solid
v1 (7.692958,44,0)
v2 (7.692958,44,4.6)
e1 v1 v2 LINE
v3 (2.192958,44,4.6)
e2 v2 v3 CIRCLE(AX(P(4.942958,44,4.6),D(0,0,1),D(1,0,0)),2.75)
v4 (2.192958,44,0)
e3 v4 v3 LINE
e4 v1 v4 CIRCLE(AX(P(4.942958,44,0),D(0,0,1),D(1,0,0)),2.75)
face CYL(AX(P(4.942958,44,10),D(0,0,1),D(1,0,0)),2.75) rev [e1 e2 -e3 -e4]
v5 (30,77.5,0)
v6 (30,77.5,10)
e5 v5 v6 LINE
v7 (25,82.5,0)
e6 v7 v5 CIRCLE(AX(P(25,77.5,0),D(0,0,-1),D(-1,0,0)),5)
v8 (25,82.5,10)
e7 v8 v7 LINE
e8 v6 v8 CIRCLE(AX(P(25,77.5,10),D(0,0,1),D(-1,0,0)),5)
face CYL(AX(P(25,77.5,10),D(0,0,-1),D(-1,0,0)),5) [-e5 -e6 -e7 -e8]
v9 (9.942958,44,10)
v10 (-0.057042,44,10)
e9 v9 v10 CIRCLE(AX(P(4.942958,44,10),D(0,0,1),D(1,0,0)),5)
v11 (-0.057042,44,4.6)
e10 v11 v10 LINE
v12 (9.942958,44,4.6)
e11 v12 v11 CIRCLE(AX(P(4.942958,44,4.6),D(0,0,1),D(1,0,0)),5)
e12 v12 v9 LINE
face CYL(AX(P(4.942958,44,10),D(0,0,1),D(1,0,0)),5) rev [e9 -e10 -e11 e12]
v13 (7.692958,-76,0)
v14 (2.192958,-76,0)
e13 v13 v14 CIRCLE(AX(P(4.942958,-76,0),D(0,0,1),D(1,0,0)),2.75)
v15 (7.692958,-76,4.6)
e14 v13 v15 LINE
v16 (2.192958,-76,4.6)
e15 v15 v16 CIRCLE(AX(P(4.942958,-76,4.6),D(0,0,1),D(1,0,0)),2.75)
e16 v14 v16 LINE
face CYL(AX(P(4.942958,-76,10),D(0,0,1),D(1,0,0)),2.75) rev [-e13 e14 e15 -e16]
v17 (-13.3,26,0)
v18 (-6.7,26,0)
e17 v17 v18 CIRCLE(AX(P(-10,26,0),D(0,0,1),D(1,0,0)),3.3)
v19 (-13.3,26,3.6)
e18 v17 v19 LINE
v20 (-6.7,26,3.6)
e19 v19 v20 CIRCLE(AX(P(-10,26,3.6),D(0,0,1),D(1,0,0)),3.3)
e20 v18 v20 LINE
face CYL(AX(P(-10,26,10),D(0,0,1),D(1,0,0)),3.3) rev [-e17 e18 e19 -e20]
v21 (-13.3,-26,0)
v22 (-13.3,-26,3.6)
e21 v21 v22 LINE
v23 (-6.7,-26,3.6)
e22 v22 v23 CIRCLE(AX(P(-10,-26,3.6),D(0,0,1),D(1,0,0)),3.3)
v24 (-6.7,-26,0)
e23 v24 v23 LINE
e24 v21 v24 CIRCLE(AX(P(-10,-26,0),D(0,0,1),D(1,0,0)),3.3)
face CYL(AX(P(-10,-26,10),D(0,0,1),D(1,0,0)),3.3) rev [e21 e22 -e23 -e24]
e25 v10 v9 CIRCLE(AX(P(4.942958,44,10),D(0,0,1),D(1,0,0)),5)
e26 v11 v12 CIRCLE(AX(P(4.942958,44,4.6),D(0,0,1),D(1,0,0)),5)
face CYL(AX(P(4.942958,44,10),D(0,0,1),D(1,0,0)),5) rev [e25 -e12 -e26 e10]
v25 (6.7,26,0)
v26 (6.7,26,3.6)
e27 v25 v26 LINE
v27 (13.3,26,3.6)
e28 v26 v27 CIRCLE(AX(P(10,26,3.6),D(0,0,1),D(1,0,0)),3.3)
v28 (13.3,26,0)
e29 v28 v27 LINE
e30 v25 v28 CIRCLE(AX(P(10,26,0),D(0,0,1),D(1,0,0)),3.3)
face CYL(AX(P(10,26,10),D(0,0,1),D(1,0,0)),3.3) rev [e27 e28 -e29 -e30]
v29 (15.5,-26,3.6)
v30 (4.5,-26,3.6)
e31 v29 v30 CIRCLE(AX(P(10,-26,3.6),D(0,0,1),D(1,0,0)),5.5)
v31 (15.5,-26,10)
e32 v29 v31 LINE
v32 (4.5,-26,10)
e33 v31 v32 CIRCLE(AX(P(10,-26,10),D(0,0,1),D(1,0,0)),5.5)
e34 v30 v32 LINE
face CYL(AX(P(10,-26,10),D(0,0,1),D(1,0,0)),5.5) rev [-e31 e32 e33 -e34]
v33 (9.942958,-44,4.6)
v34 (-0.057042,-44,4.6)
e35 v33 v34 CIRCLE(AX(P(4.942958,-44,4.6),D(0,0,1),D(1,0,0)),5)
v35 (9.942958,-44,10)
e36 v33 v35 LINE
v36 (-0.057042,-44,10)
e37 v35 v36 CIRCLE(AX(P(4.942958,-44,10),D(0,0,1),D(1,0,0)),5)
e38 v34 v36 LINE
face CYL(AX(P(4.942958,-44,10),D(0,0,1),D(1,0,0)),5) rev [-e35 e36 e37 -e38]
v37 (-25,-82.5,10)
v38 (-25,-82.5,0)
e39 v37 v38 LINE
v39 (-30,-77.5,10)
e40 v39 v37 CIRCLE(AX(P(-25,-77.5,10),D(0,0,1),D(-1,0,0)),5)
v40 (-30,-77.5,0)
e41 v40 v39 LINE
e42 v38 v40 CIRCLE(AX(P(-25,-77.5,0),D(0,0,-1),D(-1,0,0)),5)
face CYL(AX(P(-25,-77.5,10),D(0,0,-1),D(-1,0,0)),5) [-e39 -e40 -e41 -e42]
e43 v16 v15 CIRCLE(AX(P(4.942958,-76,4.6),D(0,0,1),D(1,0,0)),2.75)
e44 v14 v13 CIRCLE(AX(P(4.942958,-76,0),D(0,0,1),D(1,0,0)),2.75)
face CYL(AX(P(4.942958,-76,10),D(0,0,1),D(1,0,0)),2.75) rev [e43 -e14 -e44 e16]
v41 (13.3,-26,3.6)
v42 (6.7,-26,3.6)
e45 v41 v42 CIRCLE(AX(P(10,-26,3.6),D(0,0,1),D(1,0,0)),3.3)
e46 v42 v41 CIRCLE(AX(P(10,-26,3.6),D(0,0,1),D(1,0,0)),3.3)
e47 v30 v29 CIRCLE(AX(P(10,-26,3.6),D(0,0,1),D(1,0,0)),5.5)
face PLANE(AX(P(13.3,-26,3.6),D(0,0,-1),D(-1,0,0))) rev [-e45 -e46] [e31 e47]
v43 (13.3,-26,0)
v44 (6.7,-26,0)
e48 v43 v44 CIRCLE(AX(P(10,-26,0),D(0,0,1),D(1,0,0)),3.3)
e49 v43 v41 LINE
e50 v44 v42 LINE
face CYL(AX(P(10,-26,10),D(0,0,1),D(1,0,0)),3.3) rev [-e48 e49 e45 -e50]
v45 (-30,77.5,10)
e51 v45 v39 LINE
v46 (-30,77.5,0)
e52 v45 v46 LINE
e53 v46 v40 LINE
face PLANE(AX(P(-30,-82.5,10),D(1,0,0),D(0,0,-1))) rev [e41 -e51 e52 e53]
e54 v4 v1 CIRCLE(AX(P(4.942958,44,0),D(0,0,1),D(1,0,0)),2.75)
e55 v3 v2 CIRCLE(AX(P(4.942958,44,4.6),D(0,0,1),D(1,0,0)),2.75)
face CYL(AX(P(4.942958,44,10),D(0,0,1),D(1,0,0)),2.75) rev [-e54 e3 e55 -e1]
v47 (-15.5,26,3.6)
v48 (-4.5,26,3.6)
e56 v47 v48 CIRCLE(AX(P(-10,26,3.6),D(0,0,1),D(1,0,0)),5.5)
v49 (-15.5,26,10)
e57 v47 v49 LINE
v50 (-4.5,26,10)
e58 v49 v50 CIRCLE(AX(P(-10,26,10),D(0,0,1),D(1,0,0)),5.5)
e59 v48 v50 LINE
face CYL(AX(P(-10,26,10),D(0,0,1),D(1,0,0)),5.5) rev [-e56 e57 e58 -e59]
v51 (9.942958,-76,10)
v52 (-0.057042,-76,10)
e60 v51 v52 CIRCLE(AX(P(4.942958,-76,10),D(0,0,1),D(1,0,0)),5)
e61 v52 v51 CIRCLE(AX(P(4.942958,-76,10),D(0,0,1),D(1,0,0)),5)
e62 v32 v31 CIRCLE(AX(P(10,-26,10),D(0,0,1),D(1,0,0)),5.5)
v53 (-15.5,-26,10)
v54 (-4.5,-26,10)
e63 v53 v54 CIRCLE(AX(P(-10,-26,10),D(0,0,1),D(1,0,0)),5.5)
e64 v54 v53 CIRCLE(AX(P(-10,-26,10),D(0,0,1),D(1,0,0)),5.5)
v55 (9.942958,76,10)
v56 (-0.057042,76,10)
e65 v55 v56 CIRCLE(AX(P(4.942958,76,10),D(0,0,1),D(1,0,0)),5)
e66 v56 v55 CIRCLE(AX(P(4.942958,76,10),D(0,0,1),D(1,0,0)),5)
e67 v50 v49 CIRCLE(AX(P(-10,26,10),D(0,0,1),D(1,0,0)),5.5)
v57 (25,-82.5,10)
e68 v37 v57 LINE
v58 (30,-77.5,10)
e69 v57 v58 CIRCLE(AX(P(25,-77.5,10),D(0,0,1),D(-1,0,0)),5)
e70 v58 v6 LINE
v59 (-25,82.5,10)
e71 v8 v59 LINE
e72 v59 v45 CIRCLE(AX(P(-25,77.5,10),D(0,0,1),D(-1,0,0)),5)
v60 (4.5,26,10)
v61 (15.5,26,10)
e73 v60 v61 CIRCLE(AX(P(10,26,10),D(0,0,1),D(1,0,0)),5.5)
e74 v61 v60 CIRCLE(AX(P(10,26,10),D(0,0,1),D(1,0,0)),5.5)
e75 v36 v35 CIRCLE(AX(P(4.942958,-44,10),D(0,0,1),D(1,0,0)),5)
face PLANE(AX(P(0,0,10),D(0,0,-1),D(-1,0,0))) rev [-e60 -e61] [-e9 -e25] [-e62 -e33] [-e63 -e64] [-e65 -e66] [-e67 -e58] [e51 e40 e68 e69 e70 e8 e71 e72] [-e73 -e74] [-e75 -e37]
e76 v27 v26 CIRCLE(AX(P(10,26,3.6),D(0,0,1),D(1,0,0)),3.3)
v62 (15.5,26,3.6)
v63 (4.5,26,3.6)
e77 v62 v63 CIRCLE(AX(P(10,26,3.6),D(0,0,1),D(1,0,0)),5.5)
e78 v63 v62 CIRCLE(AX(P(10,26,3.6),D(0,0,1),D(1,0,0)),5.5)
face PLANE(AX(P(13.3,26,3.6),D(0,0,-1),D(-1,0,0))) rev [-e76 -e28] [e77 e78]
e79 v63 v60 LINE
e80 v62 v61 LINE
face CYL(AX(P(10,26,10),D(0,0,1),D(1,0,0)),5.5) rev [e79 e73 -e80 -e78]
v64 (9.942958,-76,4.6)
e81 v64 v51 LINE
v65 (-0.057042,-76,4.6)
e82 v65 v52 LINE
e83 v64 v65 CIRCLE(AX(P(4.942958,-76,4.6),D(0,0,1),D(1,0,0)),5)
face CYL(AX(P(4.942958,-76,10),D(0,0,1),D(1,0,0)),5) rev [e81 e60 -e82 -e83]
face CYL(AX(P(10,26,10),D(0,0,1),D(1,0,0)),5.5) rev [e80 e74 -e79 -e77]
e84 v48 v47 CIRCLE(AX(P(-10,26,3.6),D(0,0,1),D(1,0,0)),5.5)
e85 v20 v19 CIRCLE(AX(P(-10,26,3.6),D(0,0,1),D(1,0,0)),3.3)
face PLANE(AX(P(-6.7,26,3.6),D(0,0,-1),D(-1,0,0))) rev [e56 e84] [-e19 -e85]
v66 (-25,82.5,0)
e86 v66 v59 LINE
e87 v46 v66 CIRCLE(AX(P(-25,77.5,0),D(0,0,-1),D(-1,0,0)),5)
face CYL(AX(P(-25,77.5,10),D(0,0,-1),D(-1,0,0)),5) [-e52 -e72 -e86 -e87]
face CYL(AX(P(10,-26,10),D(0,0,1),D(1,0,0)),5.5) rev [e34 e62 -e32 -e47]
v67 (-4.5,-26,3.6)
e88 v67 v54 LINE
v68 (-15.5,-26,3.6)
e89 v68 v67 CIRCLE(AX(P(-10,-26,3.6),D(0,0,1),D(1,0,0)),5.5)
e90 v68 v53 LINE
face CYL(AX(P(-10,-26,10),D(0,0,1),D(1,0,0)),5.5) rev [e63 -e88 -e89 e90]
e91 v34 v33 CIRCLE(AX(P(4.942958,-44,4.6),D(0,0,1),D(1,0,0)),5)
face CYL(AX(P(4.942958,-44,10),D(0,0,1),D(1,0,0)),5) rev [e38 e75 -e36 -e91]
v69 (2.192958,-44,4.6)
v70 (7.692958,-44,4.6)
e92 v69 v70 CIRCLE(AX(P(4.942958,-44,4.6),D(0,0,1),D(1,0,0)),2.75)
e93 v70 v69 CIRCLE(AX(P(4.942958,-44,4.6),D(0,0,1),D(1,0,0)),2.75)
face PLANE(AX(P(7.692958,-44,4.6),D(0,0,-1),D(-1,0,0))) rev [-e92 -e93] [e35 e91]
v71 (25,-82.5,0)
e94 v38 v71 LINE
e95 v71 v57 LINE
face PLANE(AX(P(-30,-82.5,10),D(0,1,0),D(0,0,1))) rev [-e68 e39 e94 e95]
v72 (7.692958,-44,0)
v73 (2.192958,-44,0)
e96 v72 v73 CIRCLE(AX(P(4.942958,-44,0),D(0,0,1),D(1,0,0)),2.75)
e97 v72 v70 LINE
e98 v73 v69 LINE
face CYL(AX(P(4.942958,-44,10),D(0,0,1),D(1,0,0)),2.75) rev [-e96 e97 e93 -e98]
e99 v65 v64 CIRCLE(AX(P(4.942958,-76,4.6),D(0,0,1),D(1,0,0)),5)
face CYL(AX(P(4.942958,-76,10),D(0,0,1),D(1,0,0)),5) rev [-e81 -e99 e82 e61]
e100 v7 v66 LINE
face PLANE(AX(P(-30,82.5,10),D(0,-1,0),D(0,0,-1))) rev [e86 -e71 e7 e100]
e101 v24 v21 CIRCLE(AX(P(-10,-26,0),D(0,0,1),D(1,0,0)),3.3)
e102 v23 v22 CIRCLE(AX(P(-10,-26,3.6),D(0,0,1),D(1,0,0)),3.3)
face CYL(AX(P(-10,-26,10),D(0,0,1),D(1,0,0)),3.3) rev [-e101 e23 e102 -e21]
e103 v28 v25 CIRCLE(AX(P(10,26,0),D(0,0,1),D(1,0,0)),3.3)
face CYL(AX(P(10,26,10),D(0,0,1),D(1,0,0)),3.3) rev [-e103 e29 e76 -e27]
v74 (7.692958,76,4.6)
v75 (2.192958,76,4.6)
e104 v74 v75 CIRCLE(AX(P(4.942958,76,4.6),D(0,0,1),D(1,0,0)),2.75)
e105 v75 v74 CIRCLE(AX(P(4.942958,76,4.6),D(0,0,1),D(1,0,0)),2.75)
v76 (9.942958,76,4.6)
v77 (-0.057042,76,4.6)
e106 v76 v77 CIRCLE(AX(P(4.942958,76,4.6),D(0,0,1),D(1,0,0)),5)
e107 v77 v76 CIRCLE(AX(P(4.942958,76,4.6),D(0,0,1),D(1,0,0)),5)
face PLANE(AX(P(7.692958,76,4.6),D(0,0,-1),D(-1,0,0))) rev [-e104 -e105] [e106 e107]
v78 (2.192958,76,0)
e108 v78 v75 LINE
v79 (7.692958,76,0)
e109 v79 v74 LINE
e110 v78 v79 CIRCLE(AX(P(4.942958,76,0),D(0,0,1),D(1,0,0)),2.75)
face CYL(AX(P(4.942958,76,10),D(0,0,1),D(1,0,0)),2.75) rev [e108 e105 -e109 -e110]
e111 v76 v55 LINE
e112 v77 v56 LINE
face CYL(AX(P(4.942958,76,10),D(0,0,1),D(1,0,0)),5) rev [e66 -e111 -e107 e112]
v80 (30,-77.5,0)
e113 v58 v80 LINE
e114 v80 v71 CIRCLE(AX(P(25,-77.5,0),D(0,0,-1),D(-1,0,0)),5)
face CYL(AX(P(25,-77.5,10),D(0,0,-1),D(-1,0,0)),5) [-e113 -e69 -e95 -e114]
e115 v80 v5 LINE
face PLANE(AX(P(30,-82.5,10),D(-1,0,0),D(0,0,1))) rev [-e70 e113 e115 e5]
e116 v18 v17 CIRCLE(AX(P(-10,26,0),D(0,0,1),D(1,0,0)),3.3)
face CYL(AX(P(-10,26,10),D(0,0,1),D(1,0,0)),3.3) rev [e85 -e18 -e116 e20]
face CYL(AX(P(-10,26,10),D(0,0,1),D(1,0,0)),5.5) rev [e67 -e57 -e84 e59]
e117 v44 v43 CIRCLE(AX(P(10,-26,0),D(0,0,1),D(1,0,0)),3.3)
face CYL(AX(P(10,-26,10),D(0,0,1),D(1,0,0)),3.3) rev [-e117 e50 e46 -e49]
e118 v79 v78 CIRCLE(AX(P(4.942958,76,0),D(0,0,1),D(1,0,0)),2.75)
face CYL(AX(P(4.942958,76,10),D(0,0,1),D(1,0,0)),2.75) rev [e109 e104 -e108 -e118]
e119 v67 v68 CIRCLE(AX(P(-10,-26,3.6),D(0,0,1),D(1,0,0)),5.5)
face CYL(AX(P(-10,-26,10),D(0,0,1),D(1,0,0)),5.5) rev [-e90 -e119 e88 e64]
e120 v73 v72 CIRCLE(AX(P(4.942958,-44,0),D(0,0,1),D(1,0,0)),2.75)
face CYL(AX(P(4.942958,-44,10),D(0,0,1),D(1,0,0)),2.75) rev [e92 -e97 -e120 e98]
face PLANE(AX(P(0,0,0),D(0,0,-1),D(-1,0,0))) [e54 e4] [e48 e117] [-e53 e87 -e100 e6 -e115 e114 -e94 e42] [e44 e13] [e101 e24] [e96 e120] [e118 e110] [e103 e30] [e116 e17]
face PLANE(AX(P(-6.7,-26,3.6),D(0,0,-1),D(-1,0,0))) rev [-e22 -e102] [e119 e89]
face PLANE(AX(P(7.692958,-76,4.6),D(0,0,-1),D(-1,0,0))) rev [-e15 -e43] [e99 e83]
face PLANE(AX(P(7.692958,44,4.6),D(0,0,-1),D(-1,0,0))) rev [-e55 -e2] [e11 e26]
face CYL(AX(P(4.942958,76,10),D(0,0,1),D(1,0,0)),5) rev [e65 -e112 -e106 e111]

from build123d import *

# Parameters (mm, degrees)
SKETCH1_W                                           = 60
SKETCH1_H                                           = 165
BOSS_EXTRUDE1_DEPTH                                 = 10
CBORE_FOR_M6_HEX_SOCKET_HEAD_CAP_SCREW1_D           = 6.6
CBORE_FOR_M6_HEX_SOCKET_HEAD_CAP_SCREW1_CBORE_D     = 11
CBORE_FOR_M6_HEX_SOCKET_HEAD_CAP_SCREW1_CBORE_DEPTH = 6.4
CBORE_FOR_M5_HEX_SOCKET_HEAD_CAP_SCREW2_D           = 5.5
CBORE_FOR_M5_HEX_SOCKET_HEAD_CAP_SCREW2_CBORE_D     = 10
CBORE_FOR_M5_HEX_SOCKET_HEAD_CAP_SCREW2_CBORE_DEPTH = 5.4
FILLET1_R                                           = 5


with BuildPart() as part:
    # Sketch1 → Boss-Extrude1 (new body)
    with BuildSketch(Plane.XY):
        Rectangle(SKETCH1_W, SKETCH1_H)
    extrude(amount=BOSS_EXTRUDE1_DEPTH)

    # CBORE for M6 Hex Socket Head Cap Screw1 (through all)
    with Locations(Plane.XY.offset(10)):
        with Locations((-10, 26), (10, 26), (10, -26), (-10, -26)):
            CounterBoreHole(CBORE_FOR_M6_HEX_SOCKET_HEAD_CAP_SCREW1_D / 2, CBORE_FOR_M6_HEX_SOCKET_HEAD_CAP_SCREW1_CBORE_D / 2, CBORE_FOR_M6_HEX_SOCKET_HEAD_CAP_SCREW1_CBORE_DEPTH)

    # CBORE for M5 Hex Socket Head Cap Screw2 (through all)
    with Locations(Plane.XY.offset(10)):
        with Locations((4.94295756, 76), (4.94295756, 44), (4.94295756, -44), (4.94295756, -76)):
            CounterBoreHole(CBORE_FOR_M5_HEX_SOCKET_HEAD_CAP_SCREW2_D / 2, CBORE_FOR_M5_HEX_SOCKET_HEAD_CAP_SCREW2_CBORE_D / 2, CBORE_FOR_M5_HEX_SOCKET_HEAD_CAP_SCREW2_CBORE_DEPTH)

    # Fillet1
    fillet1_edges = [part.edges().sort_by_distance(p)[0] for p in [
        (30, -82.5, 5),
        (-30, -82.5, 5),
        (-30, 82.5, 5),
        (30, 82.5, 5),
    ]]
    fillet(fillet1_edges, radius=FILLET1_R)


solid = part.part
